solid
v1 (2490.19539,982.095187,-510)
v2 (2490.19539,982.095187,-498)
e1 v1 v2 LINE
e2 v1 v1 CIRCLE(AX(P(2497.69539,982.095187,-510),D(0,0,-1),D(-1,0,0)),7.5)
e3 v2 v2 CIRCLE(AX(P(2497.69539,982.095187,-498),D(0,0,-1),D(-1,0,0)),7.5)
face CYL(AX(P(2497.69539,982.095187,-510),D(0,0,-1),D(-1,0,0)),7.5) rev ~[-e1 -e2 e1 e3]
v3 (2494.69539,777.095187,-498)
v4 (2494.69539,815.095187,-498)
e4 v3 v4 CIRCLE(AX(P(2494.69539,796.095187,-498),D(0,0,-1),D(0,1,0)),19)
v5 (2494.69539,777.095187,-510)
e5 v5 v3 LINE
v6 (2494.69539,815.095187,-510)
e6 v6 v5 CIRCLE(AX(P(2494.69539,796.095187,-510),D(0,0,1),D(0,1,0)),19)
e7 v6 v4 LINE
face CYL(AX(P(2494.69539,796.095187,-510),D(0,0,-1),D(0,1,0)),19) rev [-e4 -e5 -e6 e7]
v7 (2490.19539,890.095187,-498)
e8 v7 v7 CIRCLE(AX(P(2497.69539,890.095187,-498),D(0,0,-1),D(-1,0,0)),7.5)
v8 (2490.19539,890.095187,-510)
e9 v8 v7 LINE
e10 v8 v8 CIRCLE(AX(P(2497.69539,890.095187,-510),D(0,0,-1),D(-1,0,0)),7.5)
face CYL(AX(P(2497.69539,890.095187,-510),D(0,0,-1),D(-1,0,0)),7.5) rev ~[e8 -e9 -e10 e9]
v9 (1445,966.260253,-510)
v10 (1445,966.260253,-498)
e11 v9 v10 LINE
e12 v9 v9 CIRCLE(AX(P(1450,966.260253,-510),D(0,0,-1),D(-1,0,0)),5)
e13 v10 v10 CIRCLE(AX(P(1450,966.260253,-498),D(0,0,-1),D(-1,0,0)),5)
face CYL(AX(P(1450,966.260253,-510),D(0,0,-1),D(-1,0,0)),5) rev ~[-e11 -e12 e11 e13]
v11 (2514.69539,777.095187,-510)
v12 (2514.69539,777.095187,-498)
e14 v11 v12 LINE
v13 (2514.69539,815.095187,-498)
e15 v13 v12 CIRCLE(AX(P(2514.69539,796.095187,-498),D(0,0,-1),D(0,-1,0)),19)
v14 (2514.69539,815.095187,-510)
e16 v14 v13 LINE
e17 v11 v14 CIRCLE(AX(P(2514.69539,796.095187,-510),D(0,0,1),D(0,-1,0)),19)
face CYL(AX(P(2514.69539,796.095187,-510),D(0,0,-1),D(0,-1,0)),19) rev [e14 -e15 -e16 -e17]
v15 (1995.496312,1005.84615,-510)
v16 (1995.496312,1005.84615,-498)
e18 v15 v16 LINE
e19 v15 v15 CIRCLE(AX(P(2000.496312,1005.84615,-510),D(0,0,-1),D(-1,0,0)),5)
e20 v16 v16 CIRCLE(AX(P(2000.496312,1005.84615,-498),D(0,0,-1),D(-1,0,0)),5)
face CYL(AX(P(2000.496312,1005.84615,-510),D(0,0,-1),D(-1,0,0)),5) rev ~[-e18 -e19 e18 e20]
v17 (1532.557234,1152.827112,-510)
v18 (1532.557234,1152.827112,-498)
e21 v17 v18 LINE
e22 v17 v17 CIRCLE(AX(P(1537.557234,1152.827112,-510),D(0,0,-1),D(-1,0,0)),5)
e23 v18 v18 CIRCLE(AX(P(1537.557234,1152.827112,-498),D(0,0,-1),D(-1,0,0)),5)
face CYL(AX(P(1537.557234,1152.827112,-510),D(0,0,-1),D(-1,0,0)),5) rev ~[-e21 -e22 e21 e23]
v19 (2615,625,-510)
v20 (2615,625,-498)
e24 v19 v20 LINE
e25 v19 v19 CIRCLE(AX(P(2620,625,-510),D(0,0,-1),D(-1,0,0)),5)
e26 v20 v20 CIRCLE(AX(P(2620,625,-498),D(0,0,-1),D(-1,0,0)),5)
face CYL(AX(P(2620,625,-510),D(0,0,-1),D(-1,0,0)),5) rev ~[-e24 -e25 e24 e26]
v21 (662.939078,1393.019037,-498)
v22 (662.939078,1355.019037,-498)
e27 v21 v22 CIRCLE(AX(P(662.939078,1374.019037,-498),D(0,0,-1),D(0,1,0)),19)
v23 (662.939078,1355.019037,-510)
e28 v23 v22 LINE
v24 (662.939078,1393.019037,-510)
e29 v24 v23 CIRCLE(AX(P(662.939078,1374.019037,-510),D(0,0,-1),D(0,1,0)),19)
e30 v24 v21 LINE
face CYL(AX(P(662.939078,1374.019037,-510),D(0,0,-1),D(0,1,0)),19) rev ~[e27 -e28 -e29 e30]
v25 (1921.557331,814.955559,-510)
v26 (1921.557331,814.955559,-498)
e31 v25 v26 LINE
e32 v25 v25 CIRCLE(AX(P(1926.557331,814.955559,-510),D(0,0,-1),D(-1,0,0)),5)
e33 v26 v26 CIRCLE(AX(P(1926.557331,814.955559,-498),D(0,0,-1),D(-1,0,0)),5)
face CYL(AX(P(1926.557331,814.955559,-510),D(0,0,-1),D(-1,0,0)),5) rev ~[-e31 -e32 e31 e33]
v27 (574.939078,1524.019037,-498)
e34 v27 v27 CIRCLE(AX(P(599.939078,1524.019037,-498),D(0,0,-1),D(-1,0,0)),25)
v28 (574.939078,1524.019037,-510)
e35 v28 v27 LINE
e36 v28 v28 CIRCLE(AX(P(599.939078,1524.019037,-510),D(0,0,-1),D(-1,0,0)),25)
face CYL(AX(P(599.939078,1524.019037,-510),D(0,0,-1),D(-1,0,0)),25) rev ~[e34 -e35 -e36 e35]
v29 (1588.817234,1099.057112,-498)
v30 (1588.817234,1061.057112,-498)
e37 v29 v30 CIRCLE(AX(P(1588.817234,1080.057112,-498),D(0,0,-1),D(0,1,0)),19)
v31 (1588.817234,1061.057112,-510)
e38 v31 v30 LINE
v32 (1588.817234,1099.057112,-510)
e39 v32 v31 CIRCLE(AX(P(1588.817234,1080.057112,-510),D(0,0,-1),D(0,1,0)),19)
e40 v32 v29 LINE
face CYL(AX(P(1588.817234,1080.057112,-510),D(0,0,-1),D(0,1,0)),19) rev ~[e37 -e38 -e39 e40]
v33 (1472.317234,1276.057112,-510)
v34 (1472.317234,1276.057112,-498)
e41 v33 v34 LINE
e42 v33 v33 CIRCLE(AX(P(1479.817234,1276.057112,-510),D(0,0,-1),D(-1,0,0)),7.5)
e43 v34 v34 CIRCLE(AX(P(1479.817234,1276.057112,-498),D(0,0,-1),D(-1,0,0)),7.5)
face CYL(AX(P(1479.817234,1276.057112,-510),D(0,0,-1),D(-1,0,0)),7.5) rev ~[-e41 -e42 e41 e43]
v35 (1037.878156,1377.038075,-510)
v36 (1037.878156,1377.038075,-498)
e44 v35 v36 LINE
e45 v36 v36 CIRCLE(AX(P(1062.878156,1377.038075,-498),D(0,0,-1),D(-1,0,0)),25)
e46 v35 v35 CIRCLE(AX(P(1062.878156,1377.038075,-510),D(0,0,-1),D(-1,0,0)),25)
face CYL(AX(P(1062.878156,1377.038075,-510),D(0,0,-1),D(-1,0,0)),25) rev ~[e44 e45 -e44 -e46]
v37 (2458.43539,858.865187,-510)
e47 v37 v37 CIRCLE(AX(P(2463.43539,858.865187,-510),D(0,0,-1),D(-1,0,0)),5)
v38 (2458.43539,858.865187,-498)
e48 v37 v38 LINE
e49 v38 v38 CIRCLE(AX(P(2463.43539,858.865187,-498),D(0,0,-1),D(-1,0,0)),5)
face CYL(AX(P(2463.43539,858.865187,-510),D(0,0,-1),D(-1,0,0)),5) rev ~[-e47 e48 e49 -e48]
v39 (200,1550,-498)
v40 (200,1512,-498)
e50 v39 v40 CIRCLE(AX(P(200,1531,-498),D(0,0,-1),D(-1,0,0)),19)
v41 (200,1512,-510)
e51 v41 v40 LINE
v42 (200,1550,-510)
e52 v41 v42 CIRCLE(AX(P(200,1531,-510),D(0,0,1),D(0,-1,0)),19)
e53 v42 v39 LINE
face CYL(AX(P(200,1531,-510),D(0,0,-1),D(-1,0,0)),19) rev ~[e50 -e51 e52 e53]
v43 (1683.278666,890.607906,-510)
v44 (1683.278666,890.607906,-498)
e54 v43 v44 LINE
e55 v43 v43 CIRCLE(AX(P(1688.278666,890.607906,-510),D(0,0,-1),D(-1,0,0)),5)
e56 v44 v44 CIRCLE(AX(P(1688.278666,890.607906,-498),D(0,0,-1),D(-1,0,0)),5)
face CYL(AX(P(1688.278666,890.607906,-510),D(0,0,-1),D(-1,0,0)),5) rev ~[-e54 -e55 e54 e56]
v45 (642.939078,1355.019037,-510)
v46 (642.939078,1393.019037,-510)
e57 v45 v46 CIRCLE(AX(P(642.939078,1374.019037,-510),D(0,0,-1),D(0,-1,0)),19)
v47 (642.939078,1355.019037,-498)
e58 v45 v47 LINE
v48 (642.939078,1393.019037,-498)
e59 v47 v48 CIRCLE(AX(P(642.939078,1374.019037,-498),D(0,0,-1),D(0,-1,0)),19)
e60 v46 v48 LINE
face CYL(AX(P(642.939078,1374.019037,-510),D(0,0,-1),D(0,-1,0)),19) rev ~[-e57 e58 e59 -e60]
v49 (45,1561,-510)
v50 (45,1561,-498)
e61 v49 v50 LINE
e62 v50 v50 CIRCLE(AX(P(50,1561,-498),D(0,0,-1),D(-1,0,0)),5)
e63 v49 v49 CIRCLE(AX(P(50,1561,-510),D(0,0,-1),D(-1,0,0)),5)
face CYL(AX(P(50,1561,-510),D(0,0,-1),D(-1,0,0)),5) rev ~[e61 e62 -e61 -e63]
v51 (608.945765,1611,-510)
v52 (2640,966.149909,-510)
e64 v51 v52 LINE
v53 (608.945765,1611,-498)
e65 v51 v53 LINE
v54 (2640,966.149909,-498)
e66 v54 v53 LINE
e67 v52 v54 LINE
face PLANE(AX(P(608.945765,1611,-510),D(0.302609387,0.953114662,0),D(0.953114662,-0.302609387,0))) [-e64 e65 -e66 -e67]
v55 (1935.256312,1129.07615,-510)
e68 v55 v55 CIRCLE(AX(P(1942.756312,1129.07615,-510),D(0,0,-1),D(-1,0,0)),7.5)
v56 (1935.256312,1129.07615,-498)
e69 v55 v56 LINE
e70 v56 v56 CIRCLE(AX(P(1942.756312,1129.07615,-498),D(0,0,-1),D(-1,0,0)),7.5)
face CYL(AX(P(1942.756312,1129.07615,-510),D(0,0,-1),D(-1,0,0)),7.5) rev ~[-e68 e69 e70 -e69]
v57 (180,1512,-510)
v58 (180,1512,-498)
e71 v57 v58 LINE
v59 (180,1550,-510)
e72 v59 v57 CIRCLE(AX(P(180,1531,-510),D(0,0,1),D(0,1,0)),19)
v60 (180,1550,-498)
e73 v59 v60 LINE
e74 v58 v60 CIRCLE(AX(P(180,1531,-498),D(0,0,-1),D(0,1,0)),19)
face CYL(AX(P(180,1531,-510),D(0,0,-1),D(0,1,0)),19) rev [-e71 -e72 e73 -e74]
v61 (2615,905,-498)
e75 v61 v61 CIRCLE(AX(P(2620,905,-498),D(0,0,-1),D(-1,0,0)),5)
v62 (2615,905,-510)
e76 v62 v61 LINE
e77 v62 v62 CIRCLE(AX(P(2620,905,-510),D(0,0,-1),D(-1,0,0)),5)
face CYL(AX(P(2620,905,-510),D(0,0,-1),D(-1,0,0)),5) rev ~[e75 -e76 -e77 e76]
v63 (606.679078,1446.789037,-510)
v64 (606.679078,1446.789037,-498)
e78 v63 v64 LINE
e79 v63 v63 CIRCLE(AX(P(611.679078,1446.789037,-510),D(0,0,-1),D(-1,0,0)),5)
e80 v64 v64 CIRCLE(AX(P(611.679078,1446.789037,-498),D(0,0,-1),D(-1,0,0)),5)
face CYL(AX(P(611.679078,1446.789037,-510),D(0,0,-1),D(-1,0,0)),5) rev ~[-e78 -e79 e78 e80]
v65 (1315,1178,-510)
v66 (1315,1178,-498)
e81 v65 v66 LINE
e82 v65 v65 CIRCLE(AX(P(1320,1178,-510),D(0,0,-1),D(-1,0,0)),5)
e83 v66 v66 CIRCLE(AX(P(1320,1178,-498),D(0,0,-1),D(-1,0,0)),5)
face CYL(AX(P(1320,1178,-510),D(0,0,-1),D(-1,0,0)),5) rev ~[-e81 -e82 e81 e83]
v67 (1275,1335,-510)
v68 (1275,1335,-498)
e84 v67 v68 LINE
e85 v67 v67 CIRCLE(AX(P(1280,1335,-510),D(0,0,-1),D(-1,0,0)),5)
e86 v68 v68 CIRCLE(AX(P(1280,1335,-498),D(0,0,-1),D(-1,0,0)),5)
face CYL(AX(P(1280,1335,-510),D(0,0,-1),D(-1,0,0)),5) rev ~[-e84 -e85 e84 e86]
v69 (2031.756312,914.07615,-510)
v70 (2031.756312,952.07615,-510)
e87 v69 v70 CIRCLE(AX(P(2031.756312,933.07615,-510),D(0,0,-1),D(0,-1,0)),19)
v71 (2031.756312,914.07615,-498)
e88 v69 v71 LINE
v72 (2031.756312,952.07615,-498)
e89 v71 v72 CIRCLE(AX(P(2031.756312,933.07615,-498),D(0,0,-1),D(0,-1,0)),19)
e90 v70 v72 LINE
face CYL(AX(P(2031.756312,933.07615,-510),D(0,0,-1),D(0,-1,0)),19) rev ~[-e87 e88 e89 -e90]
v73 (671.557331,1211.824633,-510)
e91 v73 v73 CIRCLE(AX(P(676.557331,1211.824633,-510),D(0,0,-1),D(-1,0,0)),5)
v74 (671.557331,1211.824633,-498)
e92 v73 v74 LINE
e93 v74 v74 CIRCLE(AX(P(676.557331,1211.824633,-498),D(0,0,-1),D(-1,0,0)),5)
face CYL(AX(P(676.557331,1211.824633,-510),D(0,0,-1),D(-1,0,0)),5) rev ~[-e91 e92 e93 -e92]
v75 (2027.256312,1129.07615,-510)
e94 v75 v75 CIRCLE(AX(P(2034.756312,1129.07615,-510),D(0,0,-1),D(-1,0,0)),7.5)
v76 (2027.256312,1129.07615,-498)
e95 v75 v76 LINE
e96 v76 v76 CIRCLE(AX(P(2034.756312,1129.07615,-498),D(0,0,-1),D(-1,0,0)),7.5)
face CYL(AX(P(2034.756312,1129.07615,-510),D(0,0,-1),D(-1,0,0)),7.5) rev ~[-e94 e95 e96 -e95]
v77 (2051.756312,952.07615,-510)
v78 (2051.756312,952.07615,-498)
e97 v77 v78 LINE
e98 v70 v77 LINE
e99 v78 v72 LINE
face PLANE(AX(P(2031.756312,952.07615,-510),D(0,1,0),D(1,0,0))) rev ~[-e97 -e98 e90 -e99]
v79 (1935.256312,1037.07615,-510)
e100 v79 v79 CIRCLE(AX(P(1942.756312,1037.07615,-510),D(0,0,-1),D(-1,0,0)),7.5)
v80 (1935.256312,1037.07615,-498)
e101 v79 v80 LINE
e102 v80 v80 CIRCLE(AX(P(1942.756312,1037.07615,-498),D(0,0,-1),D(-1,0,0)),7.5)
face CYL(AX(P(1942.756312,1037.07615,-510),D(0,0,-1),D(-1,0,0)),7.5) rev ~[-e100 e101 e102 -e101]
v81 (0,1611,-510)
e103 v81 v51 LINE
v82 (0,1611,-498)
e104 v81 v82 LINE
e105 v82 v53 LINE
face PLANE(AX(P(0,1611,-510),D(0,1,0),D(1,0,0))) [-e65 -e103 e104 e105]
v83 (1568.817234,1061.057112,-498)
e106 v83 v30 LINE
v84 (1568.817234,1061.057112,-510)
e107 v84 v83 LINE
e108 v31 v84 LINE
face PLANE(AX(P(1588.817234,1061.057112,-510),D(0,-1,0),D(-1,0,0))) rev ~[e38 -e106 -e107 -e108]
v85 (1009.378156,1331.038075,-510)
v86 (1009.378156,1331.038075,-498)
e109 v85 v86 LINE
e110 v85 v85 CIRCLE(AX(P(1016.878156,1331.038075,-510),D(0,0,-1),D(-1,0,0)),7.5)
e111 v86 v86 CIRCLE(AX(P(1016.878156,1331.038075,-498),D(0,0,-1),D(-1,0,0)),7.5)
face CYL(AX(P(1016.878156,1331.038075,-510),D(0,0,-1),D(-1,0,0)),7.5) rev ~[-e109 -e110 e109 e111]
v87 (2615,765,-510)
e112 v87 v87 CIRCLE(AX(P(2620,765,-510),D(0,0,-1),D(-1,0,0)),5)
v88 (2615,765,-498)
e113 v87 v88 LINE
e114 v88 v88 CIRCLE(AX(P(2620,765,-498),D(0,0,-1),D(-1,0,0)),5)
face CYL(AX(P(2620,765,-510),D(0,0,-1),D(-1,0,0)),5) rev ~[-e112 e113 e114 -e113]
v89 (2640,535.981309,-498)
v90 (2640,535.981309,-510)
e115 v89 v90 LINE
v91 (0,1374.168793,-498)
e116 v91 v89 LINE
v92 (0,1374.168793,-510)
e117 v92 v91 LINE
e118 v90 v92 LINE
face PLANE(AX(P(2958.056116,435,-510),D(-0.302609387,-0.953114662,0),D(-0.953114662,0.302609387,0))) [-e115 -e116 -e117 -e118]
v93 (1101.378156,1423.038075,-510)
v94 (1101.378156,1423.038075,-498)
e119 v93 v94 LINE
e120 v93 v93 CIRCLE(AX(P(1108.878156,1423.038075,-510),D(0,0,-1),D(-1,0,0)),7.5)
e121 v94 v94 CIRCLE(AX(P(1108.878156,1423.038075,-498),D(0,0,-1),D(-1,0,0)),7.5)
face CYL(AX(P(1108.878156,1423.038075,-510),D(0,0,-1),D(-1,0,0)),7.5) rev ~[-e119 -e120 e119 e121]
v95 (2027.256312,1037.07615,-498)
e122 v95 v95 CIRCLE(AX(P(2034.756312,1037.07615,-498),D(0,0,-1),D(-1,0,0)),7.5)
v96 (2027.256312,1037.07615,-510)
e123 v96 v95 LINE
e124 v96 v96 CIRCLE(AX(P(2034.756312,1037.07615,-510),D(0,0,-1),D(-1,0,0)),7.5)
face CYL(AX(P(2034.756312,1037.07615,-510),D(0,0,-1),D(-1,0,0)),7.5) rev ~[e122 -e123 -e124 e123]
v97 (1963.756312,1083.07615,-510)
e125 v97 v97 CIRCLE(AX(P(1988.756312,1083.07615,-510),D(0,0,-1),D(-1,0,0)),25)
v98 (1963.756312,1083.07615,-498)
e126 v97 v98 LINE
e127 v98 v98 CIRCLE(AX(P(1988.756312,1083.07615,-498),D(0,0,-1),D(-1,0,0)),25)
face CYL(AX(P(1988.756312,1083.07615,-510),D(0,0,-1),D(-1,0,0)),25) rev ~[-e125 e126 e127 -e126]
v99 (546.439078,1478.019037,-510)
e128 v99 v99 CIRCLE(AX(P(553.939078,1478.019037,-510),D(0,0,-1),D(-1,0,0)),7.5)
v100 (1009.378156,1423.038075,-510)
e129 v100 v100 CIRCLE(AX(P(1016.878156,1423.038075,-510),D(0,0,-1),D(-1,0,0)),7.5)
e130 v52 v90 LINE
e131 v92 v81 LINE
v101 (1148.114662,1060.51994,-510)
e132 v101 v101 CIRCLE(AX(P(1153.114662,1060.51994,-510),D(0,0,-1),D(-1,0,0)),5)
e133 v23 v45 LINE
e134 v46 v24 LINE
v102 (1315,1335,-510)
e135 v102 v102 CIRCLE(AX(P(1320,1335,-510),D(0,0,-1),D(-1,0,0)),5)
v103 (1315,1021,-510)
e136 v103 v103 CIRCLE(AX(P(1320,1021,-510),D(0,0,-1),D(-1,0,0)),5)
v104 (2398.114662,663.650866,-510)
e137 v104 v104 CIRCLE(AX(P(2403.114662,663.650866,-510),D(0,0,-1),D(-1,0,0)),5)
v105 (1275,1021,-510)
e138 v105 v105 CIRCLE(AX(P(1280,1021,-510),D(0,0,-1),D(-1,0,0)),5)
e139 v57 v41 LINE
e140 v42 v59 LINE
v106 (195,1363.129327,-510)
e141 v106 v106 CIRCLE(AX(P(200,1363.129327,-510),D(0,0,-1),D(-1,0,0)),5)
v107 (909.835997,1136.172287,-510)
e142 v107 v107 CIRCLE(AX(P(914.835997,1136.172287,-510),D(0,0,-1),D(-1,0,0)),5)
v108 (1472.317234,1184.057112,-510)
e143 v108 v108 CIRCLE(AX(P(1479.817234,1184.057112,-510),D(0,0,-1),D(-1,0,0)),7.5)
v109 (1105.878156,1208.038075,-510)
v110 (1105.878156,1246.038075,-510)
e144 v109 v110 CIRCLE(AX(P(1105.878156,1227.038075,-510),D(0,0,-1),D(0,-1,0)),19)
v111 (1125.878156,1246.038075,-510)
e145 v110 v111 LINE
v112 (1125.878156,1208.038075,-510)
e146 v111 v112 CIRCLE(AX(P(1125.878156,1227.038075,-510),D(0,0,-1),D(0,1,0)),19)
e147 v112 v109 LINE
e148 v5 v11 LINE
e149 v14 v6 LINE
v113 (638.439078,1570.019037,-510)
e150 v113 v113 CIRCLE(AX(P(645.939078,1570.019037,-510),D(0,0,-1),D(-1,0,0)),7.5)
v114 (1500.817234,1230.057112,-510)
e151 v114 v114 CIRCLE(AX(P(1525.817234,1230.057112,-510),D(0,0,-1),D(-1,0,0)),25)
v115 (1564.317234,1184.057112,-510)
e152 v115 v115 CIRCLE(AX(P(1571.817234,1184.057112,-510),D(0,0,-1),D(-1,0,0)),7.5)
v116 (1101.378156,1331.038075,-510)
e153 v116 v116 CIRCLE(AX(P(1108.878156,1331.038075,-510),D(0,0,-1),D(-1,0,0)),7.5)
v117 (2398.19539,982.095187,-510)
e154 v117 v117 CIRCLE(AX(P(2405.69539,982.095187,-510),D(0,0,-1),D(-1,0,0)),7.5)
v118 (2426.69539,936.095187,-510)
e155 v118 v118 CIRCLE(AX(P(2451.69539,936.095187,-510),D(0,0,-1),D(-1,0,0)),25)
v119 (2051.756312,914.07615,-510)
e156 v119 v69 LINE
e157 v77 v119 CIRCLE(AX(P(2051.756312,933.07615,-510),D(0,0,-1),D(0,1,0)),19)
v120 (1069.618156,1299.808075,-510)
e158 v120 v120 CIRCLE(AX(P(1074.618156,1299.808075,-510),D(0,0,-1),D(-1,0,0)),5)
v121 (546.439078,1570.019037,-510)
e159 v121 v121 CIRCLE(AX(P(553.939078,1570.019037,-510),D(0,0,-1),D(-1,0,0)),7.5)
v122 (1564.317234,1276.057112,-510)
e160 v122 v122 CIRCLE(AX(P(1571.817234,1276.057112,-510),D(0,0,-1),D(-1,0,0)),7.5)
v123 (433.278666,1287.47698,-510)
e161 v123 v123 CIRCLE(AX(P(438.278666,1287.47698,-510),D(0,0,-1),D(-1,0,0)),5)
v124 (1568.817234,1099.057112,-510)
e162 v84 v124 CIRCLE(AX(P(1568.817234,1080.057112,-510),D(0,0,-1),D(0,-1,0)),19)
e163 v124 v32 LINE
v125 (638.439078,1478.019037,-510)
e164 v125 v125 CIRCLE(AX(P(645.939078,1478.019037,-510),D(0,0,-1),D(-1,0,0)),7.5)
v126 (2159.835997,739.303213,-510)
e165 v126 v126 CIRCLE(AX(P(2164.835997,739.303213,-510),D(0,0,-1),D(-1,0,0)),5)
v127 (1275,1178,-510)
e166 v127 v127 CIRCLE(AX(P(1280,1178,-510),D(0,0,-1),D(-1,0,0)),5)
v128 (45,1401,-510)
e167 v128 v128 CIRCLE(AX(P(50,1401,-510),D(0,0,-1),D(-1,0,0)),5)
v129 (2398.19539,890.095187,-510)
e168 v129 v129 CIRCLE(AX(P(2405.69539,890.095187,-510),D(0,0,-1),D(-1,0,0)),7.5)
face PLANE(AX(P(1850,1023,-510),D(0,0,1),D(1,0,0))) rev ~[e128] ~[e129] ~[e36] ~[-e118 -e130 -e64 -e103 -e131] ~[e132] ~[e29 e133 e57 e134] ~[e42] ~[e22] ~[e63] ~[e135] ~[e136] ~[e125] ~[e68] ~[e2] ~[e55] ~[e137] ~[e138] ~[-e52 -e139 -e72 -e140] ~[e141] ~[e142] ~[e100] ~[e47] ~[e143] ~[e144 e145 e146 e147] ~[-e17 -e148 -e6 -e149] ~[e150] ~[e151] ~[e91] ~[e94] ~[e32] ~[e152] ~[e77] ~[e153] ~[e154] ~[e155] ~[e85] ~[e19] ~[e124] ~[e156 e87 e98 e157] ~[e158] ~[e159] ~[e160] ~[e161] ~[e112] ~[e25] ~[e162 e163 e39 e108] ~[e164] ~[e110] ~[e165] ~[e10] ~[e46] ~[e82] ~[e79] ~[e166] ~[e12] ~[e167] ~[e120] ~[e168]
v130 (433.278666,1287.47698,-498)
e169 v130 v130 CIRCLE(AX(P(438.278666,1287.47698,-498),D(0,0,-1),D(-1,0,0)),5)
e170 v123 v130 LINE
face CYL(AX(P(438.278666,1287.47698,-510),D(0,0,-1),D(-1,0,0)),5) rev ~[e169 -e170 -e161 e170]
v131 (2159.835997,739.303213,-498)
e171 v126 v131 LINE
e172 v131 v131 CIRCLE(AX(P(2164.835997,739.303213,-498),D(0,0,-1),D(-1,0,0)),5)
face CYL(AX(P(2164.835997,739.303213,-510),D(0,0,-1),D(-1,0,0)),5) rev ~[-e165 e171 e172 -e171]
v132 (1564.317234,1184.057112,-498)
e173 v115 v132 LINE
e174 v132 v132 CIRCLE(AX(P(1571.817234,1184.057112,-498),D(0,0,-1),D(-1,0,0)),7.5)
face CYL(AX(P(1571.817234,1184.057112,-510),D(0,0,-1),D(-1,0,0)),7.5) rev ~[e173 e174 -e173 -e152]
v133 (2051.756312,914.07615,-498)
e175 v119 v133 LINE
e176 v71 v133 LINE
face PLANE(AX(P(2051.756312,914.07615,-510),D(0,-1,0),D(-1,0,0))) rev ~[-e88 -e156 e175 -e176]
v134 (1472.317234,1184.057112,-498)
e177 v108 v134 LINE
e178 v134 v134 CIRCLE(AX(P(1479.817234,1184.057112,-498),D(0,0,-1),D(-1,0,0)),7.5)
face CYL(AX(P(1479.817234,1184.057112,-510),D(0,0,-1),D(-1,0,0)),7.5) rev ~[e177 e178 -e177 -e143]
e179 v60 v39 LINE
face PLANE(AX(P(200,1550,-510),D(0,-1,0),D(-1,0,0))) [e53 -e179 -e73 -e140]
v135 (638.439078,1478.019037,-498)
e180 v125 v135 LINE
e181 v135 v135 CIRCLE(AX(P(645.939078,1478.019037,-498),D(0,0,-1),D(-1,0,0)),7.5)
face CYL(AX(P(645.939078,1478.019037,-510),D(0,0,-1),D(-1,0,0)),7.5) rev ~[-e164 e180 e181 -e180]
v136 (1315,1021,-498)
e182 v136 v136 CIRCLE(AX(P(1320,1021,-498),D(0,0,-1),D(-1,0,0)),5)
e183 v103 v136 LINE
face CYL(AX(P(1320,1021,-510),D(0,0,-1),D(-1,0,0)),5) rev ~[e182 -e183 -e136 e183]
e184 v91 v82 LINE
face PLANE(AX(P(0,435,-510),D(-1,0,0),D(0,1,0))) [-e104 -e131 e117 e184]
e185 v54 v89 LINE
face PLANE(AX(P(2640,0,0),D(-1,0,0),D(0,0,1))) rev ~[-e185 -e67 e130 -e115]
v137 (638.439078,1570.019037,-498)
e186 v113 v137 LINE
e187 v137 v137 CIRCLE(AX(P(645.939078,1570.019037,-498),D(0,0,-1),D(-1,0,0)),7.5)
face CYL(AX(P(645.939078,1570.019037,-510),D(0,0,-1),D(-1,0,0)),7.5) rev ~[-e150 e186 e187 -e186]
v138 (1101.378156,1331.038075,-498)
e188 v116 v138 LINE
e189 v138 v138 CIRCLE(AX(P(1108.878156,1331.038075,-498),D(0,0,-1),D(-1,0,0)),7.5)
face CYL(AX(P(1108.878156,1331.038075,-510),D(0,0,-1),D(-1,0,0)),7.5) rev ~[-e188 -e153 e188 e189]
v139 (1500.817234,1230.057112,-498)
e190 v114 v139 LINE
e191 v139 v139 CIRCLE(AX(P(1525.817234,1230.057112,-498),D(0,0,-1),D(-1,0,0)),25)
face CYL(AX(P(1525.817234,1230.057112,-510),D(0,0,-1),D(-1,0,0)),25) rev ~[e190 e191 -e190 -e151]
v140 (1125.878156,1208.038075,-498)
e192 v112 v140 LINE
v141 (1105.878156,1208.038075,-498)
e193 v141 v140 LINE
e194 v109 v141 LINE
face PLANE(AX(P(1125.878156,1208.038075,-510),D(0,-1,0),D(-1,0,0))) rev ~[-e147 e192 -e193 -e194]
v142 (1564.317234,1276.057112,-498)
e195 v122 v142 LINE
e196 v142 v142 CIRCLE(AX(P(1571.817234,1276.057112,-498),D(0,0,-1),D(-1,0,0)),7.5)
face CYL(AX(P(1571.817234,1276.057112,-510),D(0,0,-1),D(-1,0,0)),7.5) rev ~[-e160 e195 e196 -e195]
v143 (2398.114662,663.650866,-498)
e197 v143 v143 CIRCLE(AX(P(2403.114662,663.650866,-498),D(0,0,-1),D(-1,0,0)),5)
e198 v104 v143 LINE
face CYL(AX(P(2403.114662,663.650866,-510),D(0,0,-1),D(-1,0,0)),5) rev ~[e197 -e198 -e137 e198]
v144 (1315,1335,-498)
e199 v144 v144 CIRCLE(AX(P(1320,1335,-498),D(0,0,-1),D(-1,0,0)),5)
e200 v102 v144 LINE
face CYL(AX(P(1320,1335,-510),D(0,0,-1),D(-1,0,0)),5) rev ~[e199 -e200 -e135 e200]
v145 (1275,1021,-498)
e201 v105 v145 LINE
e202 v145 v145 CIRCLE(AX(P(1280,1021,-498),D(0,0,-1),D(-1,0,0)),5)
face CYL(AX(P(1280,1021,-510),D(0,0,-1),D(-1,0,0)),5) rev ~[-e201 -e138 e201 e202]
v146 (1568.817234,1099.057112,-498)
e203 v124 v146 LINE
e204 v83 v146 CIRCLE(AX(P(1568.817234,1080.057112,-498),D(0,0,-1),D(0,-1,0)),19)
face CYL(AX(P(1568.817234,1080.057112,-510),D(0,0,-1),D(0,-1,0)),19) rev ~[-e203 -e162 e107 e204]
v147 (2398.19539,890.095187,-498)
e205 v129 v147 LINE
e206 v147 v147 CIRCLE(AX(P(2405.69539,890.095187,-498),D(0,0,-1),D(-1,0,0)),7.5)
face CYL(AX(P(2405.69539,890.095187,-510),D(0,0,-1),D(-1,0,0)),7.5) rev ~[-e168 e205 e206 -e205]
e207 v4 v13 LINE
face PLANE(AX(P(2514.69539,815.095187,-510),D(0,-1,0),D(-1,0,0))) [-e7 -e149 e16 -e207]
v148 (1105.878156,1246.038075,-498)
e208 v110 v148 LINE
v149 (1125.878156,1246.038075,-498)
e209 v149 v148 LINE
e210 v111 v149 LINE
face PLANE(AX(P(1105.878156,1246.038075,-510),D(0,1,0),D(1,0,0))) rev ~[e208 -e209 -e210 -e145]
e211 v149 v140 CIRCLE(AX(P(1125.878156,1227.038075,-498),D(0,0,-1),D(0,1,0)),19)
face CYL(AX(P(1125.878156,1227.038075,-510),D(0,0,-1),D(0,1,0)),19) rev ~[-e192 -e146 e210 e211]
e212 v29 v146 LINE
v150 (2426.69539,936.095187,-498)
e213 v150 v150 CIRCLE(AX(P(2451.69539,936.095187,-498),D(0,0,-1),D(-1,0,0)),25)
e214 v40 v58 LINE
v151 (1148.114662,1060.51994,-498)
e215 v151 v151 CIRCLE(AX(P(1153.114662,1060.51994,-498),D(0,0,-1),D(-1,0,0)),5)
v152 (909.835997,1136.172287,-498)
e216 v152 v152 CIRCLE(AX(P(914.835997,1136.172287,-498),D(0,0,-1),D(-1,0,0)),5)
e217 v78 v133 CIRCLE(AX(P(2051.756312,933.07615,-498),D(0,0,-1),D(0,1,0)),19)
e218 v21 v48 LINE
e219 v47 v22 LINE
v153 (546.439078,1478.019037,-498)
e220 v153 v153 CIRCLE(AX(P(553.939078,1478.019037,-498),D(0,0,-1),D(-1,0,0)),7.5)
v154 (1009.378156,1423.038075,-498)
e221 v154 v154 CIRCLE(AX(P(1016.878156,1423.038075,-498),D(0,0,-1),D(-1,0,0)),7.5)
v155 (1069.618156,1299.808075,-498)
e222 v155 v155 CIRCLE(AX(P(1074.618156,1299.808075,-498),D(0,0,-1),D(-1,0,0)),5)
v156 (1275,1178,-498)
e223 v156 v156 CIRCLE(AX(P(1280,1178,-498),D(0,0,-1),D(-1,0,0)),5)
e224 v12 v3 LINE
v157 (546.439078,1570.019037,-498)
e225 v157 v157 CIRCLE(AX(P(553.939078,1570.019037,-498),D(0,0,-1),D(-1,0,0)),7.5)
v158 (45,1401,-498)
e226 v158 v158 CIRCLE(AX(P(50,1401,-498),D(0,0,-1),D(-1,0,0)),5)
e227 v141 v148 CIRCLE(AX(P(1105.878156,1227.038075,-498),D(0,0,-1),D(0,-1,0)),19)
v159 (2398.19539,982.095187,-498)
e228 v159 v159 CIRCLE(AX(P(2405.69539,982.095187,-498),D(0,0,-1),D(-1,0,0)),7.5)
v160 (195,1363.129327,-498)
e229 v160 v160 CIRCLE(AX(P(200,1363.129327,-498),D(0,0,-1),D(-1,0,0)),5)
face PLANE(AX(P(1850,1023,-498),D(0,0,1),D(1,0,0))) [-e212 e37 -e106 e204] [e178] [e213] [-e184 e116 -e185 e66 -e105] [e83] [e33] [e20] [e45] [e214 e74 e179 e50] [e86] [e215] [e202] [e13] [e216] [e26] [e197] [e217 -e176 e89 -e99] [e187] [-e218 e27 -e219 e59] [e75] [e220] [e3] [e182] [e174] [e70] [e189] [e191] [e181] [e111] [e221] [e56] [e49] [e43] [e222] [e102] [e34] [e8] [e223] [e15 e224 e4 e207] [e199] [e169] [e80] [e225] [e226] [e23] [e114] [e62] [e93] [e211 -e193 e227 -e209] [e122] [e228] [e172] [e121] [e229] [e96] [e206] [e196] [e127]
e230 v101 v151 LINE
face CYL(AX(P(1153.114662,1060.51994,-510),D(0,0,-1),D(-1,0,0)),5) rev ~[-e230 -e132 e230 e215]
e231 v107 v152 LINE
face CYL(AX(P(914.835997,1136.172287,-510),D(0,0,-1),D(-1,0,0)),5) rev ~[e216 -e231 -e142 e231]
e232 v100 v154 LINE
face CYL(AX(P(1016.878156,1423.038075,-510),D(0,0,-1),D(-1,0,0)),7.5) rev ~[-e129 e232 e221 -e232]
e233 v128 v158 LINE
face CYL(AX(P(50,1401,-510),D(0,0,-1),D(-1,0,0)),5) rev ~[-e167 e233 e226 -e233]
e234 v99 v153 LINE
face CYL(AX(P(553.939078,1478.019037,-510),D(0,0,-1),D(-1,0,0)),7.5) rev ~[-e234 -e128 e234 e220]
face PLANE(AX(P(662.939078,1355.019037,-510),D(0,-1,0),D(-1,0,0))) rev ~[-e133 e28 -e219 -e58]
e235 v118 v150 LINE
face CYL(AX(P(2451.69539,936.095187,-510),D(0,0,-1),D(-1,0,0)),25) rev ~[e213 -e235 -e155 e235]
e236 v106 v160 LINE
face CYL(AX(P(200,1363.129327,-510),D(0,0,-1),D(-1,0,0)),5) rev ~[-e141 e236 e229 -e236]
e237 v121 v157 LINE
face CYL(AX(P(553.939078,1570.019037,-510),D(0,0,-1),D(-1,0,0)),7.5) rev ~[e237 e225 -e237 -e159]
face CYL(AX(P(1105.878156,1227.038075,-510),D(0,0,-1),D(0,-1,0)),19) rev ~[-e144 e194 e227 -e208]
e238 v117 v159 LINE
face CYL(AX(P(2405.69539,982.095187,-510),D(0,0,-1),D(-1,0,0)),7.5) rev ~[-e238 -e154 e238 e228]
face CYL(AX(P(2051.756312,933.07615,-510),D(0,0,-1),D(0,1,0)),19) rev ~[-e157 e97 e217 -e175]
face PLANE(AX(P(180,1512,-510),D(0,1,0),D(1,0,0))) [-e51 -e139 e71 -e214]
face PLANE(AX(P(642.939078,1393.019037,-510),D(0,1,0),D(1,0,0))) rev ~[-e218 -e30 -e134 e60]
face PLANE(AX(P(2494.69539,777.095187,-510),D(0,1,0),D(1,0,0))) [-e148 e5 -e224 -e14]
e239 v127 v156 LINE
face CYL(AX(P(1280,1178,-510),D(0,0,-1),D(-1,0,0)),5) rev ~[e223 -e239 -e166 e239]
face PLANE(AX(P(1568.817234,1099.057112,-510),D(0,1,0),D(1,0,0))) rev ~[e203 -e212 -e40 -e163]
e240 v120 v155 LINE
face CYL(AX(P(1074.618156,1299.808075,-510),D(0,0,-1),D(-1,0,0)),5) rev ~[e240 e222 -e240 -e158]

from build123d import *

# Parameters (mm, degrees)
SKETCH_1_W             = 3700
SKETCH_1_H             = 1176
EXTRUDE_1_DEPTH        = 12
SKETCH_2_R             = 19
SKETCH_2_R_2           = 25
CUT_EXTRUDE_1_DEPTH    = 4036.525368524
PATTERN_LINEAR_1_COUNT = 5
PATTERN_LINEAR_1_PITCH = 485.711841895
CUT_EXTRUDE_2_DEPTH    = 4036.525368524
CUT_EXTRUDE_4_DEPTH    = 4036.525368524
CUT_EXTRUDE_5_DEPTH    = 4036.525368524
PATTERN_LINEAR_2_COUNT = 6
PATTERN_LINEAR_2_PITCH = 485.711841895
SKETCH_9_R             = 7.5
CUT_EXTRUDE_11_DEPTH   = 4036.525368524
SKETCH_11_R            = 5
CUT_EXTRUDE_12_DEPTH   = 4036.525368524
PATTERN_LINEAR_3_COUNT = 5
PATTERN_LINEAR_3_PITCH = 485.711841895
SKETCH_12_R            = 5
CUT_EXTRUDE_13_DEPTH   = 3093.743927324
PATTERN_LINEAR_4_COUNT = 5
PATTERN_LINEAR_4_PITCH = 485.711841895
EXTRUDE_4_DEPTH        = 12
CUT_EXTRUDE_14_DEPTH   = 3093.743927324
PATTERN_LINEAR_5_COUNT = 4
PATTERN_LINEAR_5_PITCH = 485.711841895


with BuildPart() as part:
    # 草图1 → 凸台-拉伸1 (new body)
    with BuildSketch(Plane.XY.offset(-510)):
        with Locations((1850, 1023)):
            Rectangle(SKETCH_1_W, SKETCH_1_H)
    extrude(amount=EXTRUDE_1_DEPTH)

    # 草图2 → 切除-拉伸1 (cut, through all)
    with BuildSketch(Plane(origin=(0, 0, -510), x_dir=(-1, 0, 0), z_dir=(0, 0, -1))):
        with Locations((-200, 1531)):
            Circle(SKETCH_2_R)
        with Locations((-599.939078063, 1524.019037425)):
            Circle(SKETCH_2_R_2)
    cut_extrude_1 = extrude(amount=-CUT_EXTRUDE_1_DEPTH, mode=Mode.SUBTRACT)

    # 阵列(线性)1: 切除-拉伸1 ×5
    with Locations(*[Vector(0.9531146620938385, -0.30260938667157716, 0) * (i * PATTERN_LINEAR_1_PITCH) for i in range(1, PATTERN_LINEAR_1_COUNT)]):
        add(cut_extrude_1, mode=Mode.SUBTRACT)

    # 草图5 → 切除-拉伸2 (cut, through all)
    with BuildSketch(Plane(origin=(0, 0, -510), x_dir=(-1, 0, 0), z_dir=(0, 0, -1))):
        Polygon((-608.945764682, 1611), (-3700, 629.604934412), (-3700, 1611), align=None)
    extrude(amount=-CUT_EXTRUDE_2_DEPTH, mode=Mode.SUBTRACT)

    # 草图6 → 切除-拉伸4 (cut, through all)
    with BuildSketch(Plane(origin=(0, 0, -510), x_dir=(-1, 0, 0), z_dir=(0, 0, -1))):
        Polygon((-2958.056115955, 435), (0, 1374.16879321), (0, 435), align=None)
    extrude(amount=-CUT_EXTRUDE_4_DEPTH, mode=Mode.SUBTRACT)

    # 草图7 → 切除-拉伸5 (cut, through all)
    with BuildSketch(Plane(origin=(0, 0, -510), x_dir=(-1, 0, 0), z_dir=(0, 0, -1))):
        with BuildLine():
            Line((-200, 1550), (-180, 1550))
            ThreePointArc((-180, 1550), (-161, 1531), (-180, 1512))
            Line((-180, 1512), (-200, 1512))
            ThreePointArc((-200, 1512), (-219, 1531), (-200, 1550))
        make_face()
    cut_extrude_5 = extrude(amount=-CUT_EXTRUDE_5_DEPTH, mode=Mode.SUBTRACT)

    # 阵列(线性)2: 切除-拉伸5 ×6
    with Locations(*[Vector(0.9531146620938385, -0.30260938667157716, 0) * (i * PATTERN_LINEAR_2_PITCH) for i in range(1, PATTERN_LINEAR_2_COUNT)]):
        add(cut_extrude_5, mode=Mode.SUBTRACT)

    # 草图9 → 切除-拉伸11 (cut, through all)
    with BuildSketch(Plane(origin=(0, 0, -510), x_dir=(-1, 0, 0), z_dir=(0, 0, -1))):
        with Locations((-553.939078063, 1570.019037425)):
            Circle(SKETCH_9_R)
        with Locations((-645.939078063, 1570.019037425)):
            Circle(SKETCH_9_R)
        with Locations((-645.939078063, 1478.019037425)):
            Circle(SKETCH_9_R)
        with Locations((-553.939078063, 1478.019037425)):
            Circle(SKETCH_9_R)
    cut_extrude_11 = extrude(amount=-CUT_EXTRUDE_11_DEPTH, mode=Mode.SUBTRACT)

    # 草图11 → 切除-拉伸12 (cut, through all)
    with BuildSketch(Plane(origin=(0, 0, -510), x_dir=(-1, 0, 0), z_dir=(0, 0, -1))):
        with Locations((-2403.114662094, 663.650866112)):
            Circle(SKETCH_11_R)
        with Locations((-50, 1561)):
            Circle(SKETCH_11_R)
        with Locations((-50, 1401)):
            Circle(SKETCH_11_R)
        with Locations((-200, 1363.129326761)):
            Circle(SKETCH_11_R)
        with Locations((-438.278665523, 1287.476980093)):
            Circle(SKETCH_11_R)
        with Locations((-676.557331047, 1211.824633425)):
            Circle(SKETCH_11_R)
        with Locations((-914.83599657, 1136.172286757)):
            Circle(SKETCH_11_R)
        with Locations((-1153.114662094, 1060.519940089)):
            Circle(SKETCH_11_R)
        with Locations((-1280, 1021)):
            Circle(SKETCH_11_R)
        with Locations((-1320, 1021)):
            Circle(SKETCH_11_R)
        with Locations((-1280, 1178)):
            Circle(SKETCH_11_R)
        with Locations((-1320, 1178)):
            Circle(SKETCH_11_R)
        with Locations((-1320, 1335)):
            Circle(SKETCH_11_R)
        with Locations((-1280, 1335)):
            Circle(SKETCH_11_R)
        with Locations((-1450, 966.260252783)):
            Circle(SKETCH_11_R)
        with Locations((-1688.278665523, 890.607906115)):
            Circle(SKETCH_11_R)
        with Locations((-1926.557331047, 814.955559447)):
            Circle(SKETCH_11_R)
        with Locations((-2164.83599657, 739.30321278)):
            Circle(SKETCH_11_R)
        with Locations((-2620, 625)):
            Circle(SKETCH_11_R)
        with Locations((-2620, 765)):
            Circle(SKETCH_11_R)
        with Locations((-2620, 905)):
            Circle(SKETCH_11_R)
    extrude(amount=-CUT_EXTRUDE_12_DEPTH, mode=Mode.SUBTRACT)

    # 阵列(线性)3: 切除-拉伸11 ×5
    with Locations(*[Vector(0.9531146620938385, -0.30260938667157716, 0) * (i * PATTERN_LINEAR_3_PITCH) for i in range(1, PATTERN_LINEAR_3_COUNT)]):
        add(cut_extrude_11, mode=Mode.SUBTRACT)

    # Surface Cut 1
    split(bisect_by=Plane.ZY.offset(-2640), keep=Keep.TOP)

    # 草图12 → 切除-拉伸13 (cut, through all)
    with BuildSketch(Plane(origin=(0, 0, -510), x_dir=(-1, 0, 0), z_dir=(0, 0, -1))):
        with Locations((-611.679078063, 1446.789037425)):
            Circle(SKETCH_12_R)
    cut_extrude_13 = extrude(amount=-CUT_EXTRUDE_13_DEPTH, mode=Mode.SUBTRACT)

    # 阵列(线性)4: 切除-拉伸13 ×5
    with Locations(*[Vector(0.9531146620938385, -0.3026093866715771, 0) * (i * PATTERN_LINEAR_4_PITCH) for i in range(1, PATTERN_LINEAR_4_COUNT)]):
        add(cut_extrude_13, mode=Mode.SUBTRACT)

    # 草图15 → 凸台-拉伸4 (add, through all)
    with BuildSketch(Plane(origin=(0, 0, -510), x_dir=(-1, 0, 0), z_dir=(0, 0, -1))):
        with BuildLine():
            Line((-662.939078063, 1414.019037425), (-642.939078063, 1414.019037425))
            ThreePointArc((-642.939078063, 1414.019037425), (-612.939078063, 1384.019037425), (-642.939078063, 1354.019037425))
            Line((-642.939078063, 1354.019037425), (-662.939078063, 1354.019037425))
            ThreePointArc((-662.939078063, 1354.019037425), (-692.939078063, 1384.019037425), (-662.939078063, 1414.019037425))
        make_face()
        with BuildLine():
            Line((-1125.878156125, 1267.03807485), (-1105.878156125, 1267.03807485))
            ThreePointArc((-1105.878156125, 1267.03807485), (-1075.878156125, 1237.03807485), (-1105.878156125, 1207.03807485))
            Line((-1105.878156125, 1207.03807485), (-1125.878156125, 1207.03807485))
            ThreePointArc((-1125.878156125, 1207.03807485), (-1155.878156125, 1237.03807485), (-1125.878156125, 1267.03807485))
        make_face()
        with BuildLine():
            Line((-1588.817234188, 1120.057112275), (-1568.817234188, 1120.057112275))
            ThreePointArc((-1568.817234188, 1120.057112275), (-1538.817234188, 1090.057112275), (-1568.817234188, 1060.057112275))
            Line((-1568.817234188, 1060.057112275), (-1588.817234188, 1060.057112275))
            ThreePointArc((-1588.817234188, 1060.057112275), (-1618.817234188, 1090.057112275), (-1588.817234188, 1120.057112275))
        make_face()
        with BuildLine():
            Line((-2051.75631225, 973.0761497), (-2031.75631225, 973.0761497))
            ThreePointArc((-2031.75631225, 973.0761497), (-2001.75631225, 943.0761497), (-2031.75631225, 913.0761497))
            Line((-2031.75631225, 913.0761497), (-2051.75631225, 913.0761497))
            ThreePointArc((-2051.75631225, 913.0761497), (-2081.75631225, 943.0761497), (-2051.75631225, 973.0761497))
        make_face()
    extrude(amount=-EXTRUDE_4_DEPTH)

    # 草图14 → 切除-拉伸14 (cut, through all)
    with BuildSketch(Plane(origin=(0, 0, -510), x_dir=(-1, 0, 0), z_dir=(0, 0, -1))):
        with BuildLine():
            Line((-642.939078063, 1393.019037425), (-662.939078063, 1393.019037425))
            ThreePointArc((-662.939078063, 1393.019037425), (-681.939078063, 1374.019037425), (-662.939078063, 1355.019037425))
            Line((-662.939078063, 1355.019037425), (-642.939078063, 1355.019037425))
            ThreePointArc((-642.939078063, 1355.019037425), (-623.939078063, 1374.019037425), (-642.939078063, 1393.019037425))
        make_face()
    cut_extrude_14 = extrude(amount=-CUT_EXTRUDE_14_DEPTH, mode=Mode.SUBTRACT)

    # 阵列(线性)5: 切除-拉伸14 ×4
    with Locations(*[Vector(0.9531146620938385, -0.3026093866715771, 0) * (i * PATTERN_LINEAR_5_PITCH) for i in range(1, PATTERN_LINEAR_5_COUNT)]):
        add(cut_extrude_14, mode=Mode.SUBTRACT)


solid = part.part
